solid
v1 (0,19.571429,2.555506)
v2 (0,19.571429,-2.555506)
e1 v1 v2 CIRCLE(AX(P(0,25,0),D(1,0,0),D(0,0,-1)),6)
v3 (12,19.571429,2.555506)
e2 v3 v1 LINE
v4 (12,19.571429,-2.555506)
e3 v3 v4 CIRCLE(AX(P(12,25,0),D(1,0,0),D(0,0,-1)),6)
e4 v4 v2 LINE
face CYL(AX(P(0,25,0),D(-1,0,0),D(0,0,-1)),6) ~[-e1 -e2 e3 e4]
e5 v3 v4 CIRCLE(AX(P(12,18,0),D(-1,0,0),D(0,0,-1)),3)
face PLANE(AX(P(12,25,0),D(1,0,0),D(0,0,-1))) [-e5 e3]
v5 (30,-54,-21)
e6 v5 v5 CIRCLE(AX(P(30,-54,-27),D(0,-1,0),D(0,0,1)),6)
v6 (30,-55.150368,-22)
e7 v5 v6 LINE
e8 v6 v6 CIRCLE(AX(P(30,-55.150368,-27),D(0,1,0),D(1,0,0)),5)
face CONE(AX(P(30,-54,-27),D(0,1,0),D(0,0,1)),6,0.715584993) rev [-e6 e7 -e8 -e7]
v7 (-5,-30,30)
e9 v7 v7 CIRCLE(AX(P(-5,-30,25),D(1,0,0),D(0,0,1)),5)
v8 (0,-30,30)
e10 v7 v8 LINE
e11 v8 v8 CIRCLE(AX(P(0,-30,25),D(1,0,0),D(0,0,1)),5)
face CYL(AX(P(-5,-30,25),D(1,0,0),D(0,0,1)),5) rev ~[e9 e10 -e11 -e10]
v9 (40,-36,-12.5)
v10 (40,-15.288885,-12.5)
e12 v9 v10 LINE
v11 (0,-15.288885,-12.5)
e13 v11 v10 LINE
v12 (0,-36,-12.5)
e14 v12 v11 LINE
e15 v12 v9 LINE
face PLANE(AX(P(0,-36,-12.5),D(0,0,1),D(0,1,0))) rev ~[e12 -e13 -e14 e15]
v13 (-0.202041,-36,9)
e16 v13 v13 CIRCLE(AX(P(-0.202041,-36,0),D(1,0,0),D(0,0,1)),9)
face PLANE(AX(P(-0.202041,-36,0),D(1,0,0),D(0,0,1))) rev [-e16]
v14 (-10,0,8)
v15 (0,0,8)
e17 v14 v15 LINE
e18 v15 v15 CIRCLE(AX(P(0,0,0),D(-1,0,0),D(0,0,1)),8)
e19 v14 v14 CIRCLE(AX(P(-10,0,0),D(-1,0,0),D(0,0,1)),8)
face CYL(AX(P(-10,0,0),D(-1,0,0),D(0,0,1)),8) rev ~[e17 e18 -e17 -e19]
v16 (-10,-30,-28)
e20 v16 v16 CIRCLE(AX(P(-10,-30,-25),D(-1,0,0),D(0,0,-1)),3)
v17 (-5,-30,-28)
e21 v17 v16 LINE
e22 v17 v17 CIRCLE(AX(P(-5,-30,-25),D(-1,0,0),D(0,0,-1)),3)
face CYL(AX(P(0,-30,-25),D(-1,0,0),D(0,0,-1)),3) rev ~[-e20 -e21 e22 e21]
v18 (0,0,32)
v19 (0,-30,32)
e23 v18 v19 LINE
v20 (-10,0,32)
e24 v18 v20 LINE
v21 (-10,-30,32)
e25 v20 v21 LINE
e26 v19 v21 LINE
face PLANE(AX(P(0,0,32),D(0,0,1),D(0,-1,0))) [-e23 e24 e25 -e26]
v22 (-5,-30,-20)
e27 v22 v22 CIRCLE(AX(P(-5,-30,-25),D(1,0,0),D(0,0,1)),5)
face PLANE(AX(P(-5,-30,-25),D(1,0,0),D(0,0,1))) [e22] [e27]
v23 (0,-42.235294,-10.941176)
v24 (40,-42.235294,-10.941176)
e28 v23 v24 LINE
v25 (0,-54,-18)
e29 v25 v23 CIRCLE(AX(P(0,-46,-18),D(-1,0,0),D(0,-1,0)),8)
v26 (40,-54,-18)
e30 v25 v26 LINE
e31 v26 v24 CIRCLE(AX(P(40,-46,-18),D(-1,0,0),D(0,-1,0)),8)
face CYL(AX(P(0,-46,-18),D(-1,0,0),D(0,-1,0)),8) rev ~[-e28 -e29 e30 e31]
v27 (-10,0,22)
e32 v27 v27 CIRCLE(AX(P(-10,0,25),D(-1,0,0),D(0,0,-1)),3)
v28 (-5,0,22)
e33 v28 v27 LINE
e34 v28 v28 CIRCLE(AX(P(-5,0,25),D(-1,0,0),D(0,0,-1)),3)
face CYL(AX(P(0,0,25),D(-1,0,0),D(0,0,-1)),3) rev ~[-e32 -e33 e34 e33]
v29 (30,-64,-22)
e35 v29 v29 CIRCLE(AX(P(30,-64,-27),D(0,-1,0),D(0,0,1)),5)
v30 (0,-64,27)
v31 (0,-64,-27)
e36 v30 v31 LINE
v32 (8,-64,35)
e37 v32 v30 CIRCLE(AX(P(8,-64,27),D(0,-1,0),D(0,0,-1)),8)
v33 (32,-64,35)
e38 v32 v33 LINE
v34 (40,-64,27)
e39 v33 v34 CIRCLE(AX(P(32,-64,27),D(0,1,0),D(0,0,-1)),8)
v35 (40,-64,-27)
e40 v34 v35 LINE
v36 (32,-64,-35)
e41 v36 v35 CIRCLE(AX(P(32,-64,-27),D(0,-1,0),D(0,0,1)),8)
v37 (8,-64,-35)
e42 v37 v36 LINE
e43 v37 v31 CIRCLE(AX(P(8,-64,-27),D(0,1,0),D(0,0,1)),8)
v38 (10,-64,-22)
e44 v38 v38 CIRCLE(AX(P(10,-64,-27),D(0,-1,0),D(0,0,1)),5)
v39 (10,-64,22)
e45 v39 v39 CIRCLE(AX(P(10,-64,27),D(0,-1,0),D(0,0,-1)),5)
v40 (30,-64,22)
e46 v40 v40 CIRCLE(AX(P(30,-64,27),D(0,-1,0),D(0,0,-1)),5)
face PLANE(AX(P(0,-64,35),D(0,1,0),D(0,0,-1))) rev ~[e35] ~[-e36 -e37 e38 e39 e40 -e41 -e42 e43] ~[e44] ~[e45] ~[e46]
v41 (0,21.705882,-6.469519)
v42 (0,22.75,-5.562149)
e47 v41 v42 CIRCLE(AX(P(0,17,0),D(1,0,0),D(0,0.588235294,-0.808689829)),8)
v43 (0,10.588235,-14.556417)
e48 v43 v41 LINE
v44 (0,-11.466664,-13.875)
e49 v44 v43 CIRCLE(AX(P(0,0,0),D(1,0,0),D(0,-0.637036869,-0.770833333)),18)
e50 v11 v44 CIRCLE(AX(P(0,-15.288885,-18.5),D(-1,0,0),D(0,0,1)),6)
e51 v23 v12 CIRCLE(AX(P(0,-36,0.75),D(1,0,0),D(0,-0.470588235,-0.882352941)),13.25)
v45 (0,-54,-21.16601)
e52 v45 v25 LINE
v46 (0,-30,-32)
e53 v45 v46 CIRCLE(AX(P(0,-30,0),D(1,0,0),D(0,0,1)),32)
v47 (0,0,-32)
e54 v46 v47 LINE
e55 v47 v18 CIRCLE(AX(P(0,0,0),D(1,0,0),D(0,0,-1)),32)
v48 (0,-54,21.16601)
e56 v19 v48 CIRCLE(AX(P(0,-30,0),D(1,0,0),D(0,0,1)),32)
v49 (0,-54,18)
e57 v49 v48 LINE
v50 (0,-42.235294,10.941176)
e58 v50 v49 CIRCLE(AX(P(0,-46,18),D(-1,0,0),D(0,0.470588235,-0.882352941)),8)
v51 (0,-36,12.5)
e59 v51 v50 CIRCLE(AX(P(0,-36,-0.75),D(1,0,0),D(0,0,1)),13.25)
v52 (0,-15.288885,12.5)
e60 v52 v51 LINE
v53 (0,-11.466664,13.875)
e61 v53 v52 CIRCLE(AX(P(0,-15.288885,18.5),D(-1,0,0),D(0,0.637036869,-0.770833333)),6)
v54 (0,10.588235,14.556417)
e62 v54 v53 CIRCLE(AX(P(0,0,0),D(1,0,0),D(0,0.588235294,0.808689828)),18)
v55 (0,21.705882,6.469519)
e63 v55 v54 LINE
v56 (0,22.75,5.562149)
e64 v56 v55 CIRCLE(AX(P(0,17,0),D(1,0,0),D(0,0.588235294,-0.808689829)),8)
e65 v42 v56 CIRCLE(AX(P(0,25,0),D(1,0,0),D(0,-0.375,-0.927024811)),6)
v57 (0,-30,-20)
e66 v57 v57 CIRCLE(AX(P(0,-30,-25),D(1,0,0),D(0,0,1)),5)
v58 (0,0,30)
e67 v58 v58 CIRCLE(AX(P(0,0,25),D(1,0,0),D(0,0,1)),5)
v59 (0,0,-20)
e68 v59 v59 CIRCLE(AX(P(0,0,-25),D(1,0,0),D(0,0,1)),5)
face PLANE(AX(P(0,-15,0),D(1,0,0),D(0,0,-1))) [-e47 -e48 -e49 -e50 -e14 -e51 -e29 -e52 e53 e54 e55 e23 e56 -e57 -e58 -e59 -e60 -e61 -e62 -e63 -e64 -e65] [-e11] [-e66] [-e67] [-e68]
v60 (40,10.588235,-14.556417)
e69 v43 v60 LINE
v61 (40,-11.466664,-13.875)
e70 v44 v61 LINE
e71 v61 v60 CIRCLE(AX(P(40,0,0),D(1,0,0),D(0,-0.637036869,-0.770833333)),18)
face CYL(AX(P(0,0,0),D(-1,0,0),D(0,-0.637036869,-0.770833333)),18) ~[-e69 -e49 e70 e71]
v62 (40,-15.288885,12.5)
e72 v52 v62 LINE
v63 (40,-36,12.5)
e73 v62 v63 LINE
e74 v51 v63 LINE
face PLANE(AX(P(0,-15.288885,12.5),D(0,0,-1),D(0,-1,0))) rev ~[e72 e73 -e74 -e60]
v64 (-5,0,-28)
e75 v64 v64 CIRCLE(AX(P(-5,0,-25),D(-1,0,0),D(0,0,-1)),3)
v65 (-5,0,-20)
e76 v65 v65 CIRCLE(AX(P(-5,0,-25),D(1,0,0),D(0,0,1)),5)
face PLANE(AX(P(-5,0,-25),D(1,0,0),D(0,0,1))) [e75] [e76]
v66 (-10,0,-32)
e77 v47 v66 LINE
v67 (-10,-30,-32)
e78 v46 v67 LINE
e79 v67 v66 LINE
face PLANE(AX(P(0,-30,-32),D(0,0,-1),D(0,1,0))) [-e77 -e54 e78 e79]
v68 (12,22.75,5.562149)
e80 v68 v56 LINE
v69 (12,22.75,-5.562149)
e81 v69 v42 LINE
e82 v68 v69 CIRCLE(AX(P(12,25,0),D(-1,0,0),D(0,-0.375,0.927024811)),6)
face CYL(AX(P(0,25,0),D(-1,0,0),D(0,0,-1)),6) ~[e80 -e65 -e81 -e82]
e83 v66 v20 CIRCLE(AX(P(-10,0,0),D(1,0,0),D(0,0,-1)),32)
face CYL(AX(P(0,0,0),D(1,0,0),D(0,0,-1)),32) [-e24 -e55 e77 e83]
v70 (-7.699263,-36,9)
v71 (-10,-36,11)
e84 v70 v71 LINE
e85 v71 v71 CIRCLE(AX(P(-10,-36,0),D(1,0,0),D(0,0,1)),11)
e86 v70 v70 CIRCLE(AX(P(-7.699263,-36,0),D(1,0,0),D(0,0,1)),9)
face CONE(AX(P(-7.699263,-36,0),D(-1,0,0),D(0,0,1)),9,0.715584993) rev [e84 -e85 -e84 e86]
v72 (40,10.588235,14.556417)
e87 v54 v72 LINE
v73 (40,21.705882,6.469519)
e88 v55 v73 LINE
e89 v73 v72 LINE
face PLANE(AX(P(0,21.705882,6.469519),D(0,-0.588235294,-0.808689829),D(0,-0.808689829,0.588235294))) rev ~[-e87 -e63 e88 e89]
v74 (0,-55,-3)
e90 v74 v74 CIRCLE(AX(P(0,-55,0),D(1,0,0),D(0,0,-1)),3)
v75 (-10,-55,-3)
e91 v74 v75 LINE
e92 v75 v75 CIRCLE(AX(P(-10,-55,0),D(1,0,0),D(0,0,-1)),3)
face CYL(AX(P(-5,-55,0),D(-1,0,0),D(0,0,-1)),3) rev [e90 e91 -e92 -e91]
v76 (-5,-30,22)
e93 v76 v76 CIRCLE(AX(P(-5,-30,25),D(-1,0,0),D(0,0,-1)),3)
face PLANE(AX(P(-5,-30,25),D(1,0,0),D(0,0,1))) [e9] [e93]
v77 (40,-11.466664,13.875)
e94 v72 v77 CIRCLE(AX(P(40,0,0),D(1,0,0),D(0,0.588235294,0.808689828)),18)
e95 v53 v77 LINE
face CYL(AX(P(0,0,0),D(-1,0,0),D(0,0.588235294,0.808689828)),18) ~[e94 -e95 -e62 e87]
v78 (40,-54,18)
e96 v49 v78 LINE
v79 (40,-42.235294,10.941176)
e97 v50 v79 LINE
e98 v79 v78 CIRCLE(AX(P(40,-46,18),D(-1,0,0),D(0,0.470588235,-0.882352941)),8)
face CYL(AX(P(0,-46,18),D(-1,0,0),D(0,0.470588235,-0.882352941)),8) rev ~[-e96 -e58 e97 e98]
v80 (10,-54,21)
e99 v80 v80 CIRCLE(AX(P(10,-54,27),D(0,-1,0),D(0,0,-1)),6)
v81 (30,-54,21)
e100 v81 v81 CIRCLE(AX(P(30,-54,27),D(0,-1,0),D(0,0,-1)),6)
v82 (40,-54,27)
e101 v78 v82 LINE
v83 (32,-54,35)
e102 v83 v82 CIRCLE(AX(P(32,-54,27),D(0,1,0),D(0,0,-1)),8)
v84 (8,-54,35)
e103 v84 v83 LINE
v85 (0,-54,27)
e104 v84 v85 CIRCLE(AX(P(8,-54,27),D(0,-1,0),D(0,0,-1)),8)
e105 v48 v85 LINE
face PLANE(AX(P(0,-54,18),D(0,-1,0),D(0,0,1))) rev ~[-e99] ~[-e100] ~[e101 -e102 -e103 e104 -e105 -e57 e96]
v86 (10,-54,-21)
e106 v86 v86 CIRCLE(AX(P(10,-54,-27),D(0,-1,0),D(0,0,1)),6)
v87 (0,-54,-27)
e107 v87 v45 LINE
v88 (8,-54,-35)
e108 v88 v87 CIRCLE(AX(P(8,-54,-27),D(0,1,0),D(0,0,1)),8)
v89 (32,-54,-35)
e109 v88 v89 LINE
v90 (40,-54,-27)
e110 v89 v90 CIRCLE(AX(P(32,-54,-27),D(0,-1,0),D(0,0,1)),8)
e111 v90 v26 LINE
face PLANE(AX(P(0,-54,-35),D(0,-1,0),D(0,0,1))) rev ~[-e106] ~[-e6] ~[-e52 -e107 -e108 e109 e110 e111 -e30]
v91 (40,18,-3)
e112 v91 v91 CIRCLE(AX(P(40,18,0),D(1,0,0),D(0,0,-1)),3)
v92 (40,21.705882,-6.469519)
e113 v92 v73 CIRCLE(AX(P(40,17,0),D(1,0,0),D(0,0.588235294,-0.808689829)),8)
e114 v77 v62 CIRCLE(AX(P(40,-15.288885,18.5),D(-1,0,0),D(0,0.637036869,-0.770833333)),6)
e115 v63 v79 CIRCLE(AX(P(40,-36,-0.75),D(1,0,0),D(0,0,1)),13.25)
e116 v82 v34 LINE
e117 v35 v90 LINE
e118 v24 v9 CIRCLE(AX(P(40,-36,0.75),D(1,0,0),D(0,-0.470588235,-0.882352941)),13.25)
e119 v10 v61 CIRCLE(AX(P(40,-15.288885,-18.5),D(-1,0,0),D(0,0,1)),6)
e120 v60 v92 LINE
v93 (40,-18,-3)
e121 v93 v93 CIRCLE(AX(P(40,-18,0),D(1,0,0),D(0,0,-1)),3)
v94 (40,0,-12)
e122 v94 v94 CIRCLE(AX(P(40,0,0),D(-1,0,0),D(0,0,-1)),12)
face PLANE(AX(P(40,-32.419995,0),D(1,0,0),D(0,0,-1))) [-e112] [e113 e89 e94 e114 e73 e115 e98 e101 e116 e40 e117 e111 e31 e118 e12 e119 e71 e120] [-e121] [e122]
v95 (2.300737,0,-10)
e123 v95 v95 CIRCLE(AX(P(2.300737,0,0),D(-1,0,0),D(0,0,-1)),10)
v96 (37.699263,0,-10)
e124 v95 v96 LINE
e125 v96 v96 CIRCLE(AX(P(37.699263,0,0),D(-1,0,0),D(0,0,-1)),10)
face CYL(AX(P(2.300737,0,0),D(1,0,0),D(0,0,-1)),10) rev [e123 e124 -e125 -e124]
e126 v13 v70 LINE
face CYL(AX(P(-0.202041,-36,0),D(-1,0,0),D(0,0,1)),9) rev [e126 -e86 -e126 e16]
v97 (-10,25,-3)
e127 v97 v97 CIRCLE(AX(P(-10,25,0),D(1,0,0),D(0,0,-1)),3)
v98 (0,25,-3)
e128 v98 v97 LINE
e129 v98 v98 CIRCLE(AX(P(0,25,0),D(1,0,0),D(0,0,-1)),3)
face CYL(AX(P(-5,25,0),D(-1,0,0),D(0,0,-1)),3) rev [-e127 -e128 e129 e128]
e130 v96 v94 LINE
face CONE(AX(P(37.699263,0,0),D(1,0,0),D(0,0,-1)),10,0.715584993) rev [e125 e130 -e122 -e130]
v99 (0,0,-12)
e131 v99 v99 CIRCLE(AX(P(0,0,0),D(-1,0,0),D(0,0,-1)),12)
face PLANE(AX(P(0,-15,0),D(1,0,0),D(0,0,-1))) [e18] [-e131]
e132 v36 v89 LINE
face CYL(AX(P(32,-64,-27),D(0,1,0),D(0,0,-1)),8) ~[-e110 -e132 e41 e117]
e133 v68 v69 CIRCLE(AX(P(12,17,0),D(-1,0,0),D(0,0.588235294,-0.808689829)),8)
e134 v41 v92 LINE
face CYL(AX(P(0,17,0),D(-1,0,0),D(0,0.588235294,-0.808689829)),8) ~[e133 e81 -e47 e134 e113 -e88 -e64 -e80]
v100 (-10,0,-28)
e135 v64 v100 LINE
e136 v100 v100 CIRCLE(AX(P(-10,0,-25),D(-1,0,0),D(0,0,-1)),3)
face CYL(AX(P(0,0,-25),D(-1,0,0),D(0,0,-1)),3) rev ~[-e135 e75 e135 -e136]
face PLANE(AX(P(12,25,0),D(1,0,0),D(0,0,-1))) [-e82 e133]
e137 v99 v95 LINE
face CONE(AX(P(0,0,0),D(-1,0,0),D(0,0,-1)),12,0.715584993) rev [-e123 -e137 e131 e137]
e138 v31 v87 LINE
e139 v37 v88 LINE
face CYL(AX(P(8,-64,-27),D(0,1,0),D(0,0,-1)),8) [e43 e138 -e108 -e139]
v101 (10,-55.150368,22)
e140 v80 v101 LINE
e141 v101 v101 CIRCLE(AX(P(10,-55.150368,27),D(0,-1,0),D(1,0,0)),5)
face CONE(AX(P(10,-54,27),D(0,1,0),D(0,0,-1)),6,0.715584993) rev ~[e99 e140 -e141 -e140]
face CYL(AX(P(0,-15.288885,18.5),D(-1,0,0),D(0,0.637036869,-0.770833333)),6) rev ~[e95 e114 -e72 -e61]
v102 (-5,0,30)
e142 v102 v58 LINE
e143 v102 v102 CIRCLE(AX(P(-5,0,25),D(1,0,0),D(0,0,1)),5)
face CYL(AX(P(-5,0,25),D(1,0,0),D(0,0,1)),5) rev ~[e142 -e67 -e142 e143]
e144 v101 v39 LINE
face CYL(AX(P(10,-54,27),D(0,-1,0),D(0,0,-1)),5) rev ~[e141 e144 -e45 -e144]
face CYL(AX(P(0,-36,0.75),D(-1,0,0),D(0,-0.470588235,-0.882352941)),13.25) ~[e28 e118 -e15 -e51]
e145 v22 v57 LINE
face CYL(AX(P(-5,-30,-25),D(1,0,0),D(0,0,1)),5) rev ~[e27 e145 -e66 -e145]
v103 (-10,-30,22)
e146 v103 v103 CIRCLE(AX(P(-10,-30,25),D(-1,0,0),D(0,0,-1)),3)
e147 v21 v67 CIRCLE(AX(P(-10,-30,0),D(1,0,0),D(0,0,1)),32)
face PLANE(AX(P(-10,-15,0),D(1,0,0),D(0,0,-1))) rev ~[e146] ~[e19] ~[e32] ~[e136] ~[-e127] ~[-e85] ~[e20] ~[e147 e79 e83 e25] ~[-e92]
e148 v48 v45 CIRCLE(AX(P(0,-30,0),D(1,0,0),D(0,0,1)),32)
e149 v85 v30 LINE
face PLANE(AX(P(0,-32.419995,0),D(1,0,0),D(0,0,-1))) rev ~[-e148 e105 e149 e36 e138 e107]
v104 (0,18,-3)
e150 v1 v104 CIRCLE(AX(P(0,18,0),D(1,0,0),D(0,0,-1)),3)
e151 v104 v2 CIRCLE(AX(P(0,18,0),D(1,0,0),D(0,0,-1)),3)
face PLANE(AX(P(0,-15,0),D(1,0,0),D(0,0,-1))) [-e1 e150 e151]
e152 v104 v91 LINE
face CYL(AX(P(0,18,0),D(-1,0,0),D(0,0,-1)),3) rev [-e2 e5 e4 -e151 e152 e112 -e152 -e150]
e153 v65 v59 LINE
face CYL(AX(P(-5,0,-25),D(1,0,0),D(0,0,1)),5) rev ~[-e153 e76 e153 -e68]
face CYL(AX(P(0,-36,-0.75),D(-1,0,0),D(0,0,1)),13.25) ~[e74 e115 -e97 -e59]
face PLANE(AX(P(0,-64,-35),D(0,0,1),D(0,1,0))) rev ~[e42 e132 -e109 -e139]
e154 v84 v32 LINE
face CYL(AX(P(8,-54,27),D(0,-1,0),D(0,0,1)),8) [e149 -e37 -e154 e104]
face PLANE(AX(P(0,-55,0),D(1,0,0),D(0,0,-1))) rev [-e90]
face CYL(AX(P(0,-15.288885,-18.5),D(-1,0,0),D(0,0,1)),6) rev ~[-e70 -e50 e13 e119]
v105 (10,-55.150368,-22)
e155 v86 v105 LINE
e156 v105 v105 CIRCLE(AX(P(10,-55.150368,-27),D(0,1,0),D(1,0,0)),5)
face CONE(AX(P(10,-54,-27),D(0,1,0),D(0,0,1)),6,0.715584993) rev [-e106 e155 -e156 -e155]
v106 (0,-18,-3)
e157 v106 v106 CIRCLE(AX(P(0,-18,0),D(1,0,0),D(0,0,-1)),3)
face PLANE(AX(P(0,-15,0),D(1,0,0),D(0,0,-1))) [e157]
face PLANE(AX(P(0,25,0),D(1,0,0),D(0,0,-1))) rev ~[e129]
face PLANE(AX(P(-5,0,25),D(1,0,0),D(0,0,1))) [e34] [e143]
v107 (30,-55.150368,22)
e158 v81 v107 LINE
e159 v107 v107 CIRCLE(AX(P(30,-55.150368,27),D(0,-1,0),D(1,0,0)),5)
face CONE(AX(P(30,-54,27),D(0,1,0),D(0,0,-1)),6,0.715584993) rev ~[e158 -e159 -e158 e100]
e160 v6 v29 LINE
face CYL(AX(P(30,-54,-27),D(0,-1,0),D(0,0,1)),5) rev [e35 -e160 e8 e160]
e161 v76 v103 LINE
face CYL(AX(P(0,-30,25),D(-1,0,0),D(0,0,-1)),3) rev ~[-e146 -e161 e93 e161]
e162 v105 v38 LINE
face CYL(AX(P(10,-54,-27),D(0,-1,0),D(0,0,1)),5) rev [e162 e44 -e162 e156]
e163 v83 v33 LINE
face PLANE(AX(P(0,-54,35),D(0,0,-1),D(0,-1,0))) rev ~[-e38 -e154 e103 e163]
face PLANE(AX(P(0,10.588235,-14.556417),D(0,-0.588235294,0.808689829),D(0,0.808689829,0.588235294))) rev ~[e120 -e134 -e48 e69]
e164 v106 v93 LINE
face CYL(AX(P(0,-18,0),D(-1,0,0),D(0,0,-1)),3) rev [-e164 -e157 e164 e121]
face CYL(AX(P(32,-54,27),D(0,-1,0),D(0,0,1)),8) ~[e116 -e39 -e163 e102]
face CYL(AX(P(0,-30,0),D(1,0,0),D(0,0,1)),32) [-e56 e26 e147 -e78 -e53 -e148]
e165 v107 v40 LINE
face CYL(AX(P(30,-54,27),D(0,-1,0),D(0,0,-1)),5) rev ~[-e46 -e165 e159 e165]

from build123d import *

# Parameters (mm, degrees)
BODY_PROFILE_SKETCH_R       = 3
PUMP_BODY_40MM_DEPTH        = 40
BODY_EDGE_FILLET_R8_R       = 8
CSK_HOLE_10_D               = 10
CSK_HOLE_10_CSINK_D         = 12
CSK_HOLE_10_CSINK_ANGLE     = 82
MOUNTING_FLANGE_10MM_DEPTH  = 10
FLANGE_RELIEF_CUT_REACH     = 90.436
FLANGE_RELIEF_CUT_SKETCH_R  = 8
CBORE_HOLE_6_D              = 6
CBORE_HOLE_6_CBORE_D        = 10
CBORE_HOLE_6_CBORE_DEPTH    = 5
SKETCH16_W                  = 3
SKETCH16_H                  = 10
PLAIN_HOLE_6_X10_AT_2_COUNT = 2
PLAIN_HOLE_6_X10_AT_2_PITCH = 80
LOCATING_BOSS_SKETCH_R      = 6
LOCATING_BOSS_12MM_DEPTH    = 12


with BuildPart() as part:
    # Body Profile Sketch → Pump Body 40mm (new body)
    with BuildSketch(Plane(origin=(0, 0, 0), x_dir=(0, 0, -1), z_dir=(1, 0, 0))):
        with BuildLine():
            Line((-12.5, -15.288884851), (-12.5, -36))
            ThreePointArc((-12.5, -36), (-12.104388127, -39.213597032), (-10.941176471, -42.235294118))
            ThreePointArc((-10.941176471, -42.235294118), (-11.140056594, -50.115966043), (-18, -54))
            Line((-18, -54), (-35, -54))
            Line((-35, -54), (-35, -64))
            Line((-35, -64), (35, -64))
            Line((35, -64), (35, -54))
            Line((35, -54), (18, -54))
            ThreePointArc((18, -54), (11.140056594, -50.115966043), (10.941176471, -42.235294118))
            ThreePointArc((10.941176471, -42.235294118), (12.104388127, -39.213597032), (12.5, -36))
            Line((12.5, -36), (12.5, -15.288884851))
            ThreePointArc((12.5, -15.288884851), (12.854205105, -13.25787525), (13.875, -11.466663639))
            ThreePointArc((13.875, -11.466663639), (17.99141486, -0.555869896), (14.556416913, 10.588235294))
            Line((14.556416913, 10.588235294), (6.469518628, 21.705882353))
            ThreePointArc((6.469518628, 21.705882353), (0, 25), (-6.469518628, 21.705882353))
            Line((-6.469518628, 21.705882353), (-14.556416913, 10.588235294))
            ThreePointArc((-14.556416913, 10.588235294), (-17.99141486, -0.555869896), (-13.875, -11.466663639))
            ThreePointArc((-13.875, -11.466663639), (-12.854205105, -13.25787525), (-12.5, -15.288884851))
        make_face()
        with Locations((0, -18)):
            Circle(BODY_PROFILE_SKETCH_R, mode=Mode.SUBTRACT)
        with Locations((0, 18)):
            Circle(BODY_PROFILE_SKETCH_R, mode=Mode.SUBTRACT)
    extrude(amount=PUMP_BODY_40MM_DEPTH)

    # Body Edge Fillet R8
    body_edge_fillet_r8_edges = [part.edges().sort_by_distance(p)[0] for p in [
        (0, -59, -35),
        (0, -59, 35),
        (40, -59, 35),
        (40, -59, -35),
    ]]
    fillet(body_edge_fillet_r8_edges, radius=BODY_EDGE_FILLET_R8_R)

    # Csk Hole Ø10 (through all)
    with Locations(Plane(origin=(10, -54, 27), x_dir=(0, 0, 1), z_dir=(0, 1, 0))):
        with Locations((0, 0), (0, 20)):
            csk_hole_10 = CounterSinkHole(CSK_HOLE_10_D / 2, CSK_HOLE_10_CSINK_D / 2, counter_sink_angle=CSK_HOLE_10_CSINK_ANGLE)

    # Csk Hole Ø10 Mirror: Csk Hole Ø10 across plane
    add(csk_hole_10.mirror(Plane.XY), mode=Mode.SUBTRACT)

    # Sketch7 → Main Bore Ø20 Csk Both Ends (revolve, cut)
    with BuildSketch(Plane(origin=(40, 0, 0), x_dir=(0, 0, -1), z_dir=(0, 1, 0))):
        Polygon((0, 0), (0, 40), (12, 40), (10, 37.699263186), (10, 2.300736814), (12, 0), align=None)
    revolve(axis=Axis((46.35, 0, 0), (-1, 0, 0)), mode=Mode.SUBTRACT)

    # Mounting Flange Sketch → Mounting Flange 10mm (add)
    with BuildSketch(Plane.ZY):
        with BuildLine():
            Line((32, 0), (32, -30))
            ThreePointArc((32, -30), (0, -62), (-32, -30))
            Line((-32, -30), (-32, 0))
            ThreePointArc((-32, 0), (0, 32), (32, 0))
        make_face()
    extrude(amount=MOUNTING_FLANGE_10MM_DEPTH)

    # Flange Relief Cut Sketch → Flange Relief Cut (cut, up to next)
    with BuildSketch(Plane.ZY.offset(10), mode=Mode.PRIVATE) as flange_relief_cut_sk1:
        Circle(FLANGE_RELIEF_CUT_SKETCH_R)
    flange_relief_cut_tool1 = extrude(flange_relief_cut_sk1.sketch, amount=-FLANGE_RELIEF_CUT_REACH, mode=Mode.PRIVATE) & part.part
    add(flange_relief_cut_tool1.solids().sort_by_distance((-10, 0, 0))[0], mode=Mode.SUBTRACT)

    # Sketch9 → Flange Csk Hole Ø18 (revolve, cut)
    with BuildSketch(Plane(origin=(-10, -36, 0), x_dir=(0, 0, 1), z_dir=(0, 1, 0))):
        Polygon((0, 0), (0, 9.797958971), (9, 9.797958971), (9, 2.300736814), (11, 0), align=None)
    revolve(axis=Axis((-16.445314094, -36, 0), (1, 0, 0)), mode=Mode.SUBTRACT)

    # CBore Hole Ø6 (through all)
    with Locations(Plane(origin=(0, -30, -25), x_dir=(0, 0, 1), z_dir=(1, 0, 0))):
        with Locations((0, 0), (0, -30), (50, 0), (50, -30)):
            CounterBoreHole(CBORE_HOLE_6_D / 2, CBORE_HOLE_6_CBORE_D / 2, CBORE_HOLE_6_CBORE_DEPTH)

    # Sketch16 → Plain Hole Ø6 x10 (revolve, cut)
    with BuildSketch(Plane(origin=(0, -55, 0), x_dir=(0, 0, -1), z_dir=(0, 1, 0))):
        with Locations((1.5, 5)):
            Rectangle(SKETCH16_W, SKETCH16_H)
    plain_hole_6_x10 = revolve(axis=Axis((-110, -55, 0), (1, 0, 0)), mode=Mode.SUBTRACT)

    # Plain Hole Ø6 x10 at 2: Plain Hole Ø6 x10 ×2
    with Locations(*[(0, i * PLAIN_HOLE_6_X10_AT_2_PITCH, 0) for i in range(1, PLAIN_HOLE_6_X10_AT_2_COUNT)]):
        add(plain_hole_6_x10, mode=Mode.SUBTRACT)

    # Locating Boss Sketch → Locating Boss 12mm (add)
    with BuildSketch(Plane(origin=(0, 0, 0), x_dir=(0, 0, -1), z_dir=(1, 0, 0))):
        with Locations((0, 25)):
            Circle(LOCATING_BOSS_SKETCH_R)
    extrude(amount=LOCATING_BOSS_12MM_DEPTH)


solid = part.part
